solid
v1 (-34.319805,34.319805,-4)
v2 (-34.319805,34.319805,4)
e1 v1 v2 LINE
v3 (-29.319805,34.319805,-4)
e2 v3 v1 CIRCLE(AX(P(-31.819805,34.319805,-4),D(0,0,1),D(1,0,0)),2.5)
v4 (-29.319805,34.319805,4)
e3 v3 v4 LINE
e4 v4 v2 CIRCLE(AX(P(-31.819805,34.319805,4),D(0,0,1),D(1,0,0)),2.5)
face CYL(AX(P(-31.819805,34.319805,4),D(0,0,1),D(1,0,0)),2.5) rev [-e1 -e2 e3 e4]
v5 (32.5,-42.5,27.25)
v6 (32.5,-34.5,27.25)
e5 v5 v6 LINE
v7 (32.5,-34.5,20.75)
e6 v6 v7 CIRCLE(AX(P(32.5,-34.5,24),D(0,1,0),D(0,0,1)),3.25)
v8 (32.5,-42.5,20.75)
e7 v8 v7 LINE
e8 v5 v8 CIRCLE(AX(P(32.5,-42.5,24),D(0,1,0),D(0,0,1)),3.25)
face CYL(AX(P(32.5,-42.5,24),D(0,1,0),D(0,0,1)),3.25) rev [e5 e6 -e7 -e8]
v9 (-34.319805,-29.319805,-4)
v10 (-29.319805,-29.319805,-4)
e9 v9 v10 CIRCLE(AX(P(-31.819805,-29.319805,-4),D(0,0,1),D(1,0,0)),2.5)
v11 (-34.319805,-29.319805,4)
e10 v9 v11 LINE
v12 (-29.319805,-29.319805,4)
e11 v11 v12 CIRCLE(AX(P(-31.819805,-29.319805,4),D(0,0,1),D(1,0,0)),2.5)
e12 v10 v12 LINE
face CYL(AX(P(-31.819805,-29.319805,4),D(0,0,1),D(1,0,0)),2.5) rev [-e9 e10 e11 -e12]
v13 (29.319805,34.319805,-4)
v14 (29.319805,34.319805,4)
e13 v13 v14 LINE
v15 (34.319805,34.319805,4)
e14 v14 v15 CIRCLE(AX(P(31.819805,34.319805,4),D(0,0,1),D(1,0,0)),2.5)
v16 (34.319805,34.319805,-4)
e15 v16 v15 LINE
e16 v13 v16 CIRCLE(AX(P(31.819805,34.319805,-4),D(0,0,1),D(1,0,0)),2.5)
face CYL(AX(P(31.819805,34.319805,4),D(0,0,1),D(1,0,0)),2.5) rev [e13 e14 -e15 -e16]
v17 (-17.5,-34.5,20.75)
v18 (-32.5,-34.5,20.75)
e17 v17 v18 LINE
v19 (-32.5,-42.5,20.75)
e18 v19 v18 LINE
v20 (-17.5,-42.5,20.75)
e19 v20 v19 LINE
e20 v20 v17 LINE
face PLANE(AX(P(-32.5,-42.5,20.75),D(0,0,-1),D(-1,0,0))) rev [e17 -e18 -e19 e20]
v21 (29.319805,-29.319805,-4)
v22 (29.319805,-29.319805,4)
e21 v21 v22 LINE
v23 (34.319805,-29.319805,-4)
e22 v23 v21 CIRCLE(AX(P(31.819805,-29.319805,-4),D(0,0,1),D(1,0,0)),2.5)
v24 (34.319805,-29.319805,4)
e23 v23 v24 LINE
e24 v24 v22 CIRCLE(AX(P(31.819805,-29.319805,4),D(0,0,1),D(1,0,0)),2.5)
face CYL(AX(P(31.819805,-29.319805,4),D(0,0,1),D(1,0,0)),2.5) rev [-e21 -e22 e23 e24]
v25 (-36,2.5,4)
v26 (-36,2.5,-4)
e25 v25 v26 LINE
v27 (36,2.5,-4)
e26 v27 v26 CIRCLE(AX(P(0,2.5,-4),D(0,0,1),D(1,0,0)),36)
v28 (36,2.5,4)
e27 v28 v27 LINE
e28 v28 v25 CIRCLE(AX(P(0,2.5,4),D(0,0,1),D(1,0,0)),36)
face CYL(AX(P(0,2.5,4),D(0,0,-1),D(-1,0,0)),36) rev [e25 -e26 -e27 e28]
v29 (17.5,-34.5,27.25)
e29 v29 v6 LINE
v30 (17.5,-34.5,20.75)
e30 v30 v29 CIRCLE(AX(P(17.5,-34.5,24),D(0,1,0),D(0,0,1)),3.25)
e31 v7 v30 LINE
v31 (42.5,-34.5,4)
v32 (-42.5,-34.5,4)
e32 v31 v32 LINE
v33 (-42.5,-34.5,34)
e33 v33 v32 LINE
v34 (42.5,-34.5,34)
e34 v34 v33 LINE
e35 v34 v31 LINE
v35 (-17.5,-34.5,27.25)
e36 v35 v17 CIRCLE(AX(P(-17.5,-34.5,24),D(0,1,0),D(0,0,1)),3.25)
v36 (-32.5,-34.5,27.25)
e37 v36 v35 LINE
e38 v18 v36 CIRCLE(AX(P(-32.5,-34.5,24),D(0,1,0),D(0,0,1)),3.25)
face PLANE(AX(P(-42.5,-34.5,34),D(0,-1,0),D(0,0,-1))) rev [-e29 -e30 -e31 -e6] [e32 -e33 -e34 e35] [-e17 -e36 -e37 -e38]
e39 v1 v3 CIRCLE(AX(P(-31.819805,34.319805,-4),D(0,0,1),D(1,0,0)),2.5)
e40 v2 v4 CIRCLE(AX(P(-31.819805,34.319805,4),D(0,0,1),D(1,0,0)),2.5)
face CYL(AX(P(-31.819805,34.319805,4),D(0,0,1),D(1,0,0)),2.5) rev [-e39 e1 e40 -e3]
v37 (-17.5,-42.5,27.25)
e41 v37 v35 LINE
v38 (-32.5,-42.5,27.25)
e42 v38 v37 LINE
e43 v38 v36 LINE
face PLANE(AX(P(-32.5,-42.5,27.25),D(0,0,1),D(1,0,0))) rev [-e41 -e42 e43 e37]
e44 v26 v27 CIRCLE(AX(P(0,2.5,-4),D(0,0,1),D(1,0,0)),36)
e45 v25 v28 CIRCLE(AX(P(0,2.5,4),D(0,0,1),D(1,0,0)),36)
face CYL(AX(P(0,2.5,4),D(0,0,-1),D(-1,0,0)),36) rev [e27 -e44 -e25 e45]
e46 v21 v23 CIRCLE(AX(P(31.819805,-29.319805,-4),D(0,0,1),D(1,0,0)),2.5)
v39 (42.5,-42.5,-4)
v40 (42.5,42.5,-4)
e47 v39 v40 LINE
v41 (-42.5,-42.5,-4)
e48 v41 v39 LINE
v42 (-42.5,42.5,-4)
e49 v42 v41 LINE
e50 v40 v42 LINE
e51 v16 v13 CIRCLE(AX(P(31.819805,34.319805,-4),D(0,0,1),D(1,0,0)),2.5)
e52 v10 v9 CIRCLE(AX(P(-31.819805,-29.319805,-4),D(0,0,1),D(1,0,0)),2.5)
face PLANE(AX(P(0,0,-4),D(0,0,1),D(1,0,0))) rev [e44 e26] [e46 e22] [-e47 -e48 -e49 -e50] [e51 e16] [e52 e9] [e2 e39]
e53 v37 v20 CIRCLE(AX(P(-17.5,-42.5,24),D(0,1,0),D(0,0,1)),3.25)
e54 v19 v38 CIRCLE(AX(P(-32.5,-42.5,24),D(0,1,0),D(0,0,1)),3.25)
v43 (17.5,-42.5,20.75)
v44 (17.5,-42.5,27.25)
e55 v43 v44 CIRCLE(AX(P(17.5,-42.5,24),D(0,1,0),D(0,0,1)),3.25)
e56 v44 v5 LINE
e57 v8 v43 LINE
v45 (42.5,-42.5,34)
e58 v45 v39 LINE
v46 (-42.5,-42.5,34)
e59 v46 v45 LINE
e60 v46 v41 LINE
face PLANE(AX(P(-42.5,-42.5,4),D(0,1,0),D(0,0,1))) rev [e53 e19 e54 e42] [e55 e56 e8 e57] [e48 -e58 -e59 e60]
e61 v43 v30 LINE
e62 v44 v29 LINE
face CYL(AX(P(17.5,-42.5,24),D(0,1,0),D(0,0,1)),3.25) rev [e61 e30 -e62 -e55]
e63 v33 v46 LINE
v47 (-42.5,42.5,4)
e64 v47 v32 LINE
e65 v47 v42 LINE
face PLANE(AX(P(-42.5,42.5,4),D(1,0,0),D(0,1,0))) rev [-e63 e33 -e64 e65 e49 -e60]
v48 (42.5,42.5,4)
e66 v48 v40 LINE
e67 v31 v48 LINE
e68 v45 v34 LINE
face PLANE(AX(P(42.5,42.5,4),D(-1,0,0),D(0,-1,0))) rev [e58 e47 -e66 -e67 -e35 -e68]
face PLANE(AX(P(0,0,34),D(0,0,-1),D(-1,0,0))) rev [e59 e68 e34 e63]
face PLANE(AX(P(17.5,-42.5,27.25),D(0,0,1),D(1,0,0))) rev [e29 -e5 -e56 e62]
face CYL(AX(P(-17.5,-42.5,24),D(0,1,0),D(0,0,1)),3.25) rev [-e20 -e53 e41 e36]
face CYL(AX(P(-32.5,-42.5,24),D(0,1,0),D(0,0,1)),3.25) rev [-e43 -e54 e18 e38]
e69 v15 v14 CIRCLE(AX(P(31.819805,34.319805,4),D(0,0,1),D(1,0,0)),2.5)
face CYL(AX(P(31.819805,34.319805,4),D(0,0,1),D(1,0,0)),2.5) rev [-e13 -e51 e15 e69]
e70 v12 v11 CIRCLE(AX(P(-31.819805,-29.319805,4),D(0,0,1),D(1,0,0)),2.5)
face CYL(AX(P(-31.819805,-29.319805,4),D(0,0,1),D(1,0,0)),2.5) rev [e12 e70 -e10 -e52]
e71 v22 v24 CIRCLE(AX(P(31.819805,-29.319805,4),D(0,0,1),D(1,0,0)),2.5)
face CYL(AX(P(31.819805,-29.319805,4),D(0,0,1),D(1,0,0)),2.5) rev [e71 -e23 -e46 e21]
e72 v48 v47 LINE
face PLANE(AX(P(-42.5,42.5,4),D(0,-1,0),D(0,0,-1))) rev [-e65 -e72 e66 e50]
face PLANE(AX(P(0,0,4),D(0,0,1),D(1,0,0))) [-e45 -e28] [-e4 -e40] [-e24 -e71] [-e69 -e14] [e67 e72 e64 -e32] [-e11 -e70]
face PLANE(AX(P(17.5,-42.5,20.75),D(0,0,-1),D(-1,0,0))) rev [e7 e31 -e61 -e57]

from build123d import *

# Parameters (mm, degrees)
SKETCH_1_W          = 85
SKETCH_1_H          = 85
SKETCH_1_R          = 36
EXTRUDE_1_DEPTH     = 4
HOLE_WIZARD_M6_1_D  = 5
SKETCH_4_W          = 85
SKETCH_4_H          = 8
EXTRUDE_2_DEPTH     = 30
CUT_EXTRUDE_1_DEPTH = 95.293425009


with BuildPart() as part:
    # 草图1 → 凸台-拉伸1 (new, symmetric)
    with BuildSketch(Plane.XY):
        Rectangle(SKETCH_1_W, SKETCH_1_H)
        with Locations((0, 2.5)):
            Circle(SKETCH_1_R, mode=Mode.SUBTRACT)
    extrude(amount=EXTRUDE_1_DEPTH, both=True)

    # M6 螺纹孔1 (through all)
    with Locations(Plane(origin=(-31.819805153, 34.319805153, 4), x_dir=(1, 0, 0), z_dir=(0, 0, 1))):
        with Locations((0, 0), (63.639610306, -63.639610306), (0, -63.639610306), (63.639610306, 0)):
            Hole(HOLE_WIZARD_M6_1_D / 2)

    # 草图4 → 凸台-拉伸2 (add)
    with BuildSketch(Plane.XY.offset(4)):
        with Locations((0, -38.5)):
            Rectangle(SKETCH_4_W, SKETCH_4_H)
    extrude(amount=EXTRUDE_2_DEPTH)

    # 草图5 → 切除-拉伸1 (cut, through all)
    with BuildSketch(Plane(origin=(0, -34.5, 0), x_dir=(1, 0, 0), z_dir=(0, 1, 0))):
        with BuildLine():
            Line((-32.5, -20.75), (-17.5, -20.75))
            ThreePointArc((-17.5, -20.75), (-14.25, -24), (-17.5, -27.25))
            Line((-17.5, -27.25), (-32.5, -27.25))
            ThreePointArc((-32.5, -27.25), (-35.75, -24), (-32.5, -20.75))
        make_face()
        with BuildLine():
            Line((17.5, -20.75), (32.5, -20.75))
            ThreePointArc((32.5, -20.75), (35.75, -24), (32.5, -27.25))
            Line((32.5, -27.25), (17.5, -27.25))
            ThreePointArc((17.5, -27.25), (14.25, -24), (17.5, -20.75))
        make_face()
    extrude(amount=-CUT_EXTRUDE_1_DEPTH, mode=Mode.SUBTRACT)


solid = part.part
